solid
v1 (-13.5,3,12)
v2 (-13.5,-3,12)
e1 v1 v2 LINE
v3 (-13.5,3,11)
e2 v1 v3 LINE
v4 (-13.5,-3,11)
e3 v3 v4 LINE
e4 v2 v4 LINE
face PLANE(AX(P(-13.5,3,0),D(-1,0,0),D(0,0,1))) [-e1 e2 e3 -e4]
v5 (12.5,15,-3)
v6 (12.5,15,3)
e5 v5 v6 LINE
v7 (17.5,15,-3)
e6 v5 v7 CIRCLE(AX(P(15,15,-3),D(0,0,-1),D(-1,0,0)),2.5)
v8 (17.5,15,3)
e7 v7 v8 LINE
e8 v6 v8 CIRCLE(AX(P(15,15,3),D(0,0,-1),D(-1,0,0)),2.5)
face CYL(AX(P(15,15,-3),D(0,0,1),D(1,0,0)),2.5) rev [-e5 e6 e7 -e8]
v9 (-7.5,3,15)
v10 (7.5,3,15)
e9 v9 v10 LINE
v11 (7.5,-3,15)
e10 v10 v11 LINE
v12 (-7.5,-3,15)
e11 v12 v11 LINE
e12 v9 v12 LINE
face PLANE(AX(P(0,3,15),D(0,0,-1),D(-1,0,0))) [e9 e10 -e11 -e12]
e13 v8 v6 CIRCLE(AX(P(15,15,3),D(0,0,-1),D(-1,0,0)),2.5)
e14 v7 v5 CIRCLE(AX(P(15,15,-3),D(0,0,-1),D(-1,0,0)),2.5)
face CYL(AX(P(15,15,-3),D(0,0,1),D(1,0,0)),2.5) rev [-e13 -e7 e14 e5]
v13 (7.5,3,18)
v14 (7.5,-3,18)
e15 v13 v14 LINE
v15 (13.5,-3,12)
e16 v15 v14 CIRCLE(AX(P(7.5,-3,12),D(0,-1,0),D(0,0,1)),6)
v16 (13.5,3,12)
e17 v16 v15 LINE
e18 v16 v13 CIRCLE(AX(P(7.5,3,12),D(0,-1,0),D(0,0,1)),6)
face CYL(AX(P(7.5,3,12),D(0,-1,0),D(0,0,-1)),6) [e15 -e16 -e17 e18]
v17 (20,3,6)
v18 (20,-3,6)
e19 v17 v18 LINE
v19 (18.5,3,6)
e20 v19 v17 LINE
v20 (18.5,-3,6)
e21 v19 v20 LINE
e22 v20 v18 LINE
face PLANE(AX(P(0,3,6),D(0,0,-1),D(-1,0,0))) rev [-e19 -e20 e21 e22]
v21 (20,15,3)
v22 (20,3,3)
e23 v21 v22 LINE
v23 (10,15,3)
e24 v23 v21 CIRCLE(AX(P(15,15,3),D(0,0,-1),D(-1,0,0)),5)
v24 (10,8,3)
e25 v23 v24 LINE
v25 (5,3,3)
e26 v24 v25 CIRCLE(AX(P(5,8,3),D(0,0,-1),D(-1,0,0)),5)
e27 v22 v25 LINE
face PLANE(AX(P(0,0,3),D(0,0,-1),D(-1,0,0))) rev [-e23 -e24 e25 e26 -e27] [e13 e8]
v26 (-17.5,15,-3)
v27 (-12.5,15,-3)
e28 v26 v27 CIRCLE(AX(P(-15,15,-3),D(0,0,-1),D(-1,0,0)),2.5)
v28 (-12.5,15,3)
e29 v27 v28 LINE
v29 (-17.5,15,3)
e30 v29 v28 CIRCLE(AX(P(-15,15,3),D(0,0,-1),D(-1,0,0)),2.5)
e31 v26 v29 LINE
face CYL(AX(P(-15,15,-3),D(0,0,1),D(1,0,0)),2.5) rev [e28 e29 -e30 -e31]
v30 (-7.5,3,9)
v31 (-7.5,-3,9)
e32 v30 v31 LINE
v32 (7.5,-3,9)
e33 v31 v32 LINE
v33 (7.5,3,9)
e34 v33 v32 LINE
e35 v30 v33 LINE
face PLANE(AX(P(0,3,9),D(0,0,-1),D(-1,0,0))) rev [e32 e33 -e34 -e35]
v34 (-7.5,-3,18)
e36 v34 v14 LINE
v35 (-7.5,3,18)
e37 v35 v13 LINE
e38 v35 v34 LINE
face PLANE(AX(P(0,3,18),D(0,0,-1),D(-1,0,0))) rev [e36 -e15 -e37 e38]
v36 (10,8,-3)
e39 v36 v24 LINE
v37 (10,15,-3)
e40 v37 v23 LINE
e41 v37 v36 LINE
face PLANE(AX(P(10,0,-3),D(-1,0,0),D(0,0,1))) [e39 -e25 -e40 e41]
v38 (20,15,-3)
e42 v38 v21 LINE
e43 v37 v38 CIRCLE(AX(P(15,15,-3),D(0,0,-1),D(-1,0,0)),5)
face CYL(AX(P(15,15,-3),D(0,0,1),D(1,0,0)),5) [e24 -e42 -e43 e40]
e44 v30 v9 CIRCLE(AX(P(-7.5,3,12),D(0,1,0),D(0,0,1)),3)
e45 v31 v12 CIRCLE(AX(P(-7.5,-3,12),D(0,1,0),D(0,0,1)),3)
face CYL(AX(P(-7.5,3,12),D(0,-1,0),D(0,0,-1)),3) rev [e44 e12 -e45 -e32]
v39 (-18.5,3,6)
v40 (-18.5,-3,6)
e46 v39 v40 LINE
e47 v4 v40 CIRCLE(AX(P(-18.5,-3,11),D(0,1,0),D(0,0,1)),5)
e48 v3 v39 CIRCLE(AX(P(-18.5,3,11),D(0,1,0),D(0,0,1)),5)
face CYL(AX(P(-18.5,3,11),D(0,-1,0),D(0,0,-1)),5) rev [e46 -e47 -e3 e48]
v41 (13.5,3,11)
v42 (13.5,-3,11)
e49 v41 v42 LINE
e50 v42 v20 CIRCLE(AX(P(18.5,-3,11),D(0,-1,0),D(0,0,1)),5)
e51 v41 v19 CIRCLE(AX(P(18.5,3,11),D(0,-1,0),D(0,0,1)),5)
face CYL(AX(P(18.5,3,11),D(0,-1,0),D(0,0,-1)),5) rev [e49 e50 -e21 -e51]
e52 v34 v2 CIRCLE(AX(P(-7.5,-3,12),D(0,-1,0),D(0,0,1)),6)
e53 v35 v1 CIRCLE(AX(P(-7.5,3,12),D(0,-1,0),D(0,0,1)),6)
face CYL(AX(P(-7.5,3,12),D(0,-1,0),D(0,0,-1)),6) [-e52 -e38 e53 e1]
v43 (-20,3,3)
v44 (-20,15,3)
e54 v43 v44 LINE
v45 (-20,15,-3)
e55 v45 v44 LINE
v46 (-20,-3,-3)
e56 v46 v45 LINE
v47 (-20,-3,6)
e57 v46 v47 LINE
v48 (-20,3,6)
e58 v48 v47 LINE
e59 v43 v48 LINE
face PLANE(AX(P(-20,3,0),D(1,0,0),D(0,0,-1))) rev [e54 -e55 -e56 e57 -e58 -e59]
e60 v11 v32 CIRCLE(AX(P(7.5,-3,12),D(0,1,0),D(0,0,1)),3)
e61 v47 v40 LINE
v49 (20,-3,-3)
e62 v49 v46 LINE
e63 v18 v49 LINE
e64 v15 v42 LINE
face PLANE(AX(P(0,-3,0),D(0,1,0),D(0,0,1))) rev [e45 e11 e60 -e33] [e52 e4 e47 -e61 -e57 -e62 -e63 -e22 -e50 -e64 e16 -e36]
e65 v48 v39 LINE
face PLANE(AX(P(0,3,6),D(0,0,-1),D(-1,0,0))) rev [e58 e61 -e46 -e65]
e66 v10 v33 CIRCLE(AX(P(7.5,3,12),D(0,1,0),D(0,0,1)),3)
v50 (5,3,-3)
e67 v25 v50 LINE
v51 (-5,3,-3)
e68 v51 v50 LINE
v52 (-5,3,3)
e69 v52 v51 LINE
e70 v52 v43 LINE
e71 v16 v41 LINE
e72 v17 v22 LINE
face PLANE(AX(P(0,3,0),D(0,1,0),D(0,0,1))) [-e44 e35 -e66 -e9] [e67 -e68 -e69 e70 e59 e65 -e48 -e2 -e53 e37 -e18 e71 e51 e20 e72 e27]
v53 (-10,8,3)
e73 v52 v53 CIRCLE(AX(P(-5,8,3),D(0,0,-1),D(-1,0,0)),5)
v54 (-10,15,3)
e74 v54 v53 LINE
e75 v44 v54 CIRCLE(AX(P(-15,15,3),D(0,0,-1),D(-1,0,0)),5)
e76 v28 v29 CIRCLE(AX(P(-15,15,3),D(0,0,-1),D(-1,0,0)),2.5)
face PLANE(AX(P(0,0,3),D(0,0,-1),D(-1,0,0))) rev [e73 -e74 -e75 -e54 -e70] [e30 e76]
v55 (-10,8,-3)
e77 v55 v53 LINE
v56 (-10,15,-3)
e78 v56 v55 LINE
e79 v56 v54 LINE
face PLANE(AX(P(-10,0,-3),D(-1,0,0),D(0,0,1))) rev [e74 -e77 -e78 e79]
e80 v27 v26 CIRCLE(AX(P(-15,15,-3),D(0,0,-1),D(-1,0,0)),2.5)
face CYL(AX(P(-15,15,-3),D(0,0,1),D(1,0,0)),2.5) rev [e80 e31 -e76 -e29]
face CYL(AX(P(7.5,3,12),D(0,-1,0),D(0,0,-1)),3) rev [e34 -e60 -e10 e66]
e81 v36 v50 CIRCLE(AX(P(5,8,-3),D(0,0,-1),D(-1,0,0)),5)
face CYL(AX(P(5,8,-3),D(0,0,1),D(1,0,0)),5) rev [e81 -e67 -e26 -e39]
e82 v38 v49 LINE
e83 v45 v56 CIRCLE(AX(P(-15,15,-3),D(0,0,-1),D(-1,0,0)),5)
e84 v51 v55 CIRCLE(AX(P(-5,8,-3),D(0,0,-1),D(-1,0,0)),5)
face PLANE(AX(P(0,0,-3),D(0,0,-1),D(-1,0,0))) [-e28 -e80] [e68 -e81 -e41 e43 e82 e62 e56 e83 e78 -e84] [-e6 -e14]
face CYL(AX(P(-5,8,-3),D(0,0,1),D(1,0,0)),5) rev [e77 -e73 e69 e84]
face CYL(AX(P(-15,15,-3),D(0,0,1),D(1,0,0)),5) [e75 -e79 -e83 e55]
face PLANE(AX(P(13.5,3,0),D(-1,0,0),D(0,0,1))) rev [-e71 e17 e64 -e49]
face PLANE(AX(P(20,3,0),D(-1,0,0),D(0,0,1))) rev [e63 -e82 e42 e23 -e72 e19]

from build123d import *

# Parameters (mm, degrees)
BASE_PLATE_DEPTH        = 3
CLEVIS_LUGS_PROFILE_W   = 40
CLEVIS_LUGS_PROFILE_H   = 6
CLEVIS_LUGS_PROFILE_R   = 5
CLEVIS_LUGS_PROFILE_R_2 = 2.5
CLEVIS_LUGS_DEPTH       = 3


with BuildPart() as part:
    # Base Plate Profile → Base Plate (new, symmetric)
    with BuildSketch(Plane(origin=(0, 0, 0), x_dir=(1, 0, 0), z_dir=(0, 1, 0))):
        with BuildLine():
            Line((-20, 0), (20, 0))
            Line((20, 0), (20, -6))
            Line((20, -6), (18.5, -6))
            ThreePointArc((18.5, -6), (14.964466094, -7.464466094), (13.5, -11))
            Line((13.5, -11), (13.5, -12))
            ThreePointArc((13.5, -12), (11.742640687, -16.242640687), (7.5, -18))
            Line((7.5, -18), (-7.5, -18))
            ThreePointArc((-7.5, -18), (-11.742640687, -16.242640687), (-13.5, -12))
            Line((-13.5, -12), (-13.5, -11))
            ThreePointArc((-13.5, -11), (-14.964466094, -7.464466094), (-18.5, -6))
            Line((-18.5, -6), (-20, -6))
            Line((-20, -6), (-20, 0))
        make_face()
        with BuildLine():
            Line((-7.5, -9), (7.5, -9))
            ThreePointArc((7.5, -9), (10.5, -12), (7.5, -15))
            Line((7.5, -15), (-7.5, -15))
            ThreePointArc((-7.5, -15), (-10.5, -12), (-7.5, -9))
        make_face(mode=Mode.SUBTRACT)
    extrude(amount=BASE_PLATE_DEPTH, both=True)

    # Clevis Lugs Profile → Clevis Lugs (add, symmetric)
    # profile 1 of 5: a face of its own
    with BuildSketch(Plane(origin=(0, 0, 0), x_dir=(-1, 0, 0), z_dir=(0, 0, -1))):
        Rectangle(CLEVIS_LUGS_PROFILE_W, CLEVIS_LUGS_PROFILE_H)
    # profile 2 of 5: a face of its own
    with BuildSketch(Plane(origin=(0, 0, 0), x_dir=(-1, 0, 0), z_dir=(0, 0, -1))):
        with BuildLine():
            Line((-20, 15), (-20, 3))
            Line((-20, 3), (-5, 3))
            ThreePointArc((-5, 3), (-8.535533906, 4.464466094), (-10, 8))
            Line((-10, 8), (-10, 15))
            ThreePointArc((-10, 15), (-15, 10), (-20, 15))
        make_face()
    # profile 3 of 5: a face of its own
    with BuildSketch(Plane(origin=(0, 0, 0), x_dir=(-1, 0, 0), z_dir=(0, 0, -1))):
        with BuildLine():
            Line((5, 3), (20, 3))
            Line((20, 3), (20, 15))
            ThreePointArc((20, 15), (15, 10), (10, 15))
            Line((10, 15), (10, 8))
            ThreePointArc((10, 8), (8.535533906, 4.464466094), (5, 3))
        make_face()
    # profile 4 of 5: a face of its own
    with BuildSketch(Plane(origin=(0, 0, 0), x_dir=(-1, 0, 0), z_dir=(0, 0, -1))):
        with Locations((15, 15)):
            Circle(CLEVIS_LUGS_PROFILE_R)
        with Locations((15, 15)):
            Circle(CLEVIS_LUGS_PROFILE_R_2, mode=Mode.SUBTRACT)
    # profile 5 of 5: a face of its own
    with BuildSketch(Plane(origin=(0, 0, 0), x_dir=(-1, 0, 0), z_dir=(0, 0, -1))):
        with Locations((-15, 15)):
            Circle(CLEVIS_LUGS_PROFILE_R)
        with Locations((-15, 15)):
            Circle(CLEVIS_LUGS_PROFILE_R_2, mode=Mode.SUBTRACT)
    extrude(amount=CLEVIS_LUGS_DEPTH, both=True)


solid = part.part
